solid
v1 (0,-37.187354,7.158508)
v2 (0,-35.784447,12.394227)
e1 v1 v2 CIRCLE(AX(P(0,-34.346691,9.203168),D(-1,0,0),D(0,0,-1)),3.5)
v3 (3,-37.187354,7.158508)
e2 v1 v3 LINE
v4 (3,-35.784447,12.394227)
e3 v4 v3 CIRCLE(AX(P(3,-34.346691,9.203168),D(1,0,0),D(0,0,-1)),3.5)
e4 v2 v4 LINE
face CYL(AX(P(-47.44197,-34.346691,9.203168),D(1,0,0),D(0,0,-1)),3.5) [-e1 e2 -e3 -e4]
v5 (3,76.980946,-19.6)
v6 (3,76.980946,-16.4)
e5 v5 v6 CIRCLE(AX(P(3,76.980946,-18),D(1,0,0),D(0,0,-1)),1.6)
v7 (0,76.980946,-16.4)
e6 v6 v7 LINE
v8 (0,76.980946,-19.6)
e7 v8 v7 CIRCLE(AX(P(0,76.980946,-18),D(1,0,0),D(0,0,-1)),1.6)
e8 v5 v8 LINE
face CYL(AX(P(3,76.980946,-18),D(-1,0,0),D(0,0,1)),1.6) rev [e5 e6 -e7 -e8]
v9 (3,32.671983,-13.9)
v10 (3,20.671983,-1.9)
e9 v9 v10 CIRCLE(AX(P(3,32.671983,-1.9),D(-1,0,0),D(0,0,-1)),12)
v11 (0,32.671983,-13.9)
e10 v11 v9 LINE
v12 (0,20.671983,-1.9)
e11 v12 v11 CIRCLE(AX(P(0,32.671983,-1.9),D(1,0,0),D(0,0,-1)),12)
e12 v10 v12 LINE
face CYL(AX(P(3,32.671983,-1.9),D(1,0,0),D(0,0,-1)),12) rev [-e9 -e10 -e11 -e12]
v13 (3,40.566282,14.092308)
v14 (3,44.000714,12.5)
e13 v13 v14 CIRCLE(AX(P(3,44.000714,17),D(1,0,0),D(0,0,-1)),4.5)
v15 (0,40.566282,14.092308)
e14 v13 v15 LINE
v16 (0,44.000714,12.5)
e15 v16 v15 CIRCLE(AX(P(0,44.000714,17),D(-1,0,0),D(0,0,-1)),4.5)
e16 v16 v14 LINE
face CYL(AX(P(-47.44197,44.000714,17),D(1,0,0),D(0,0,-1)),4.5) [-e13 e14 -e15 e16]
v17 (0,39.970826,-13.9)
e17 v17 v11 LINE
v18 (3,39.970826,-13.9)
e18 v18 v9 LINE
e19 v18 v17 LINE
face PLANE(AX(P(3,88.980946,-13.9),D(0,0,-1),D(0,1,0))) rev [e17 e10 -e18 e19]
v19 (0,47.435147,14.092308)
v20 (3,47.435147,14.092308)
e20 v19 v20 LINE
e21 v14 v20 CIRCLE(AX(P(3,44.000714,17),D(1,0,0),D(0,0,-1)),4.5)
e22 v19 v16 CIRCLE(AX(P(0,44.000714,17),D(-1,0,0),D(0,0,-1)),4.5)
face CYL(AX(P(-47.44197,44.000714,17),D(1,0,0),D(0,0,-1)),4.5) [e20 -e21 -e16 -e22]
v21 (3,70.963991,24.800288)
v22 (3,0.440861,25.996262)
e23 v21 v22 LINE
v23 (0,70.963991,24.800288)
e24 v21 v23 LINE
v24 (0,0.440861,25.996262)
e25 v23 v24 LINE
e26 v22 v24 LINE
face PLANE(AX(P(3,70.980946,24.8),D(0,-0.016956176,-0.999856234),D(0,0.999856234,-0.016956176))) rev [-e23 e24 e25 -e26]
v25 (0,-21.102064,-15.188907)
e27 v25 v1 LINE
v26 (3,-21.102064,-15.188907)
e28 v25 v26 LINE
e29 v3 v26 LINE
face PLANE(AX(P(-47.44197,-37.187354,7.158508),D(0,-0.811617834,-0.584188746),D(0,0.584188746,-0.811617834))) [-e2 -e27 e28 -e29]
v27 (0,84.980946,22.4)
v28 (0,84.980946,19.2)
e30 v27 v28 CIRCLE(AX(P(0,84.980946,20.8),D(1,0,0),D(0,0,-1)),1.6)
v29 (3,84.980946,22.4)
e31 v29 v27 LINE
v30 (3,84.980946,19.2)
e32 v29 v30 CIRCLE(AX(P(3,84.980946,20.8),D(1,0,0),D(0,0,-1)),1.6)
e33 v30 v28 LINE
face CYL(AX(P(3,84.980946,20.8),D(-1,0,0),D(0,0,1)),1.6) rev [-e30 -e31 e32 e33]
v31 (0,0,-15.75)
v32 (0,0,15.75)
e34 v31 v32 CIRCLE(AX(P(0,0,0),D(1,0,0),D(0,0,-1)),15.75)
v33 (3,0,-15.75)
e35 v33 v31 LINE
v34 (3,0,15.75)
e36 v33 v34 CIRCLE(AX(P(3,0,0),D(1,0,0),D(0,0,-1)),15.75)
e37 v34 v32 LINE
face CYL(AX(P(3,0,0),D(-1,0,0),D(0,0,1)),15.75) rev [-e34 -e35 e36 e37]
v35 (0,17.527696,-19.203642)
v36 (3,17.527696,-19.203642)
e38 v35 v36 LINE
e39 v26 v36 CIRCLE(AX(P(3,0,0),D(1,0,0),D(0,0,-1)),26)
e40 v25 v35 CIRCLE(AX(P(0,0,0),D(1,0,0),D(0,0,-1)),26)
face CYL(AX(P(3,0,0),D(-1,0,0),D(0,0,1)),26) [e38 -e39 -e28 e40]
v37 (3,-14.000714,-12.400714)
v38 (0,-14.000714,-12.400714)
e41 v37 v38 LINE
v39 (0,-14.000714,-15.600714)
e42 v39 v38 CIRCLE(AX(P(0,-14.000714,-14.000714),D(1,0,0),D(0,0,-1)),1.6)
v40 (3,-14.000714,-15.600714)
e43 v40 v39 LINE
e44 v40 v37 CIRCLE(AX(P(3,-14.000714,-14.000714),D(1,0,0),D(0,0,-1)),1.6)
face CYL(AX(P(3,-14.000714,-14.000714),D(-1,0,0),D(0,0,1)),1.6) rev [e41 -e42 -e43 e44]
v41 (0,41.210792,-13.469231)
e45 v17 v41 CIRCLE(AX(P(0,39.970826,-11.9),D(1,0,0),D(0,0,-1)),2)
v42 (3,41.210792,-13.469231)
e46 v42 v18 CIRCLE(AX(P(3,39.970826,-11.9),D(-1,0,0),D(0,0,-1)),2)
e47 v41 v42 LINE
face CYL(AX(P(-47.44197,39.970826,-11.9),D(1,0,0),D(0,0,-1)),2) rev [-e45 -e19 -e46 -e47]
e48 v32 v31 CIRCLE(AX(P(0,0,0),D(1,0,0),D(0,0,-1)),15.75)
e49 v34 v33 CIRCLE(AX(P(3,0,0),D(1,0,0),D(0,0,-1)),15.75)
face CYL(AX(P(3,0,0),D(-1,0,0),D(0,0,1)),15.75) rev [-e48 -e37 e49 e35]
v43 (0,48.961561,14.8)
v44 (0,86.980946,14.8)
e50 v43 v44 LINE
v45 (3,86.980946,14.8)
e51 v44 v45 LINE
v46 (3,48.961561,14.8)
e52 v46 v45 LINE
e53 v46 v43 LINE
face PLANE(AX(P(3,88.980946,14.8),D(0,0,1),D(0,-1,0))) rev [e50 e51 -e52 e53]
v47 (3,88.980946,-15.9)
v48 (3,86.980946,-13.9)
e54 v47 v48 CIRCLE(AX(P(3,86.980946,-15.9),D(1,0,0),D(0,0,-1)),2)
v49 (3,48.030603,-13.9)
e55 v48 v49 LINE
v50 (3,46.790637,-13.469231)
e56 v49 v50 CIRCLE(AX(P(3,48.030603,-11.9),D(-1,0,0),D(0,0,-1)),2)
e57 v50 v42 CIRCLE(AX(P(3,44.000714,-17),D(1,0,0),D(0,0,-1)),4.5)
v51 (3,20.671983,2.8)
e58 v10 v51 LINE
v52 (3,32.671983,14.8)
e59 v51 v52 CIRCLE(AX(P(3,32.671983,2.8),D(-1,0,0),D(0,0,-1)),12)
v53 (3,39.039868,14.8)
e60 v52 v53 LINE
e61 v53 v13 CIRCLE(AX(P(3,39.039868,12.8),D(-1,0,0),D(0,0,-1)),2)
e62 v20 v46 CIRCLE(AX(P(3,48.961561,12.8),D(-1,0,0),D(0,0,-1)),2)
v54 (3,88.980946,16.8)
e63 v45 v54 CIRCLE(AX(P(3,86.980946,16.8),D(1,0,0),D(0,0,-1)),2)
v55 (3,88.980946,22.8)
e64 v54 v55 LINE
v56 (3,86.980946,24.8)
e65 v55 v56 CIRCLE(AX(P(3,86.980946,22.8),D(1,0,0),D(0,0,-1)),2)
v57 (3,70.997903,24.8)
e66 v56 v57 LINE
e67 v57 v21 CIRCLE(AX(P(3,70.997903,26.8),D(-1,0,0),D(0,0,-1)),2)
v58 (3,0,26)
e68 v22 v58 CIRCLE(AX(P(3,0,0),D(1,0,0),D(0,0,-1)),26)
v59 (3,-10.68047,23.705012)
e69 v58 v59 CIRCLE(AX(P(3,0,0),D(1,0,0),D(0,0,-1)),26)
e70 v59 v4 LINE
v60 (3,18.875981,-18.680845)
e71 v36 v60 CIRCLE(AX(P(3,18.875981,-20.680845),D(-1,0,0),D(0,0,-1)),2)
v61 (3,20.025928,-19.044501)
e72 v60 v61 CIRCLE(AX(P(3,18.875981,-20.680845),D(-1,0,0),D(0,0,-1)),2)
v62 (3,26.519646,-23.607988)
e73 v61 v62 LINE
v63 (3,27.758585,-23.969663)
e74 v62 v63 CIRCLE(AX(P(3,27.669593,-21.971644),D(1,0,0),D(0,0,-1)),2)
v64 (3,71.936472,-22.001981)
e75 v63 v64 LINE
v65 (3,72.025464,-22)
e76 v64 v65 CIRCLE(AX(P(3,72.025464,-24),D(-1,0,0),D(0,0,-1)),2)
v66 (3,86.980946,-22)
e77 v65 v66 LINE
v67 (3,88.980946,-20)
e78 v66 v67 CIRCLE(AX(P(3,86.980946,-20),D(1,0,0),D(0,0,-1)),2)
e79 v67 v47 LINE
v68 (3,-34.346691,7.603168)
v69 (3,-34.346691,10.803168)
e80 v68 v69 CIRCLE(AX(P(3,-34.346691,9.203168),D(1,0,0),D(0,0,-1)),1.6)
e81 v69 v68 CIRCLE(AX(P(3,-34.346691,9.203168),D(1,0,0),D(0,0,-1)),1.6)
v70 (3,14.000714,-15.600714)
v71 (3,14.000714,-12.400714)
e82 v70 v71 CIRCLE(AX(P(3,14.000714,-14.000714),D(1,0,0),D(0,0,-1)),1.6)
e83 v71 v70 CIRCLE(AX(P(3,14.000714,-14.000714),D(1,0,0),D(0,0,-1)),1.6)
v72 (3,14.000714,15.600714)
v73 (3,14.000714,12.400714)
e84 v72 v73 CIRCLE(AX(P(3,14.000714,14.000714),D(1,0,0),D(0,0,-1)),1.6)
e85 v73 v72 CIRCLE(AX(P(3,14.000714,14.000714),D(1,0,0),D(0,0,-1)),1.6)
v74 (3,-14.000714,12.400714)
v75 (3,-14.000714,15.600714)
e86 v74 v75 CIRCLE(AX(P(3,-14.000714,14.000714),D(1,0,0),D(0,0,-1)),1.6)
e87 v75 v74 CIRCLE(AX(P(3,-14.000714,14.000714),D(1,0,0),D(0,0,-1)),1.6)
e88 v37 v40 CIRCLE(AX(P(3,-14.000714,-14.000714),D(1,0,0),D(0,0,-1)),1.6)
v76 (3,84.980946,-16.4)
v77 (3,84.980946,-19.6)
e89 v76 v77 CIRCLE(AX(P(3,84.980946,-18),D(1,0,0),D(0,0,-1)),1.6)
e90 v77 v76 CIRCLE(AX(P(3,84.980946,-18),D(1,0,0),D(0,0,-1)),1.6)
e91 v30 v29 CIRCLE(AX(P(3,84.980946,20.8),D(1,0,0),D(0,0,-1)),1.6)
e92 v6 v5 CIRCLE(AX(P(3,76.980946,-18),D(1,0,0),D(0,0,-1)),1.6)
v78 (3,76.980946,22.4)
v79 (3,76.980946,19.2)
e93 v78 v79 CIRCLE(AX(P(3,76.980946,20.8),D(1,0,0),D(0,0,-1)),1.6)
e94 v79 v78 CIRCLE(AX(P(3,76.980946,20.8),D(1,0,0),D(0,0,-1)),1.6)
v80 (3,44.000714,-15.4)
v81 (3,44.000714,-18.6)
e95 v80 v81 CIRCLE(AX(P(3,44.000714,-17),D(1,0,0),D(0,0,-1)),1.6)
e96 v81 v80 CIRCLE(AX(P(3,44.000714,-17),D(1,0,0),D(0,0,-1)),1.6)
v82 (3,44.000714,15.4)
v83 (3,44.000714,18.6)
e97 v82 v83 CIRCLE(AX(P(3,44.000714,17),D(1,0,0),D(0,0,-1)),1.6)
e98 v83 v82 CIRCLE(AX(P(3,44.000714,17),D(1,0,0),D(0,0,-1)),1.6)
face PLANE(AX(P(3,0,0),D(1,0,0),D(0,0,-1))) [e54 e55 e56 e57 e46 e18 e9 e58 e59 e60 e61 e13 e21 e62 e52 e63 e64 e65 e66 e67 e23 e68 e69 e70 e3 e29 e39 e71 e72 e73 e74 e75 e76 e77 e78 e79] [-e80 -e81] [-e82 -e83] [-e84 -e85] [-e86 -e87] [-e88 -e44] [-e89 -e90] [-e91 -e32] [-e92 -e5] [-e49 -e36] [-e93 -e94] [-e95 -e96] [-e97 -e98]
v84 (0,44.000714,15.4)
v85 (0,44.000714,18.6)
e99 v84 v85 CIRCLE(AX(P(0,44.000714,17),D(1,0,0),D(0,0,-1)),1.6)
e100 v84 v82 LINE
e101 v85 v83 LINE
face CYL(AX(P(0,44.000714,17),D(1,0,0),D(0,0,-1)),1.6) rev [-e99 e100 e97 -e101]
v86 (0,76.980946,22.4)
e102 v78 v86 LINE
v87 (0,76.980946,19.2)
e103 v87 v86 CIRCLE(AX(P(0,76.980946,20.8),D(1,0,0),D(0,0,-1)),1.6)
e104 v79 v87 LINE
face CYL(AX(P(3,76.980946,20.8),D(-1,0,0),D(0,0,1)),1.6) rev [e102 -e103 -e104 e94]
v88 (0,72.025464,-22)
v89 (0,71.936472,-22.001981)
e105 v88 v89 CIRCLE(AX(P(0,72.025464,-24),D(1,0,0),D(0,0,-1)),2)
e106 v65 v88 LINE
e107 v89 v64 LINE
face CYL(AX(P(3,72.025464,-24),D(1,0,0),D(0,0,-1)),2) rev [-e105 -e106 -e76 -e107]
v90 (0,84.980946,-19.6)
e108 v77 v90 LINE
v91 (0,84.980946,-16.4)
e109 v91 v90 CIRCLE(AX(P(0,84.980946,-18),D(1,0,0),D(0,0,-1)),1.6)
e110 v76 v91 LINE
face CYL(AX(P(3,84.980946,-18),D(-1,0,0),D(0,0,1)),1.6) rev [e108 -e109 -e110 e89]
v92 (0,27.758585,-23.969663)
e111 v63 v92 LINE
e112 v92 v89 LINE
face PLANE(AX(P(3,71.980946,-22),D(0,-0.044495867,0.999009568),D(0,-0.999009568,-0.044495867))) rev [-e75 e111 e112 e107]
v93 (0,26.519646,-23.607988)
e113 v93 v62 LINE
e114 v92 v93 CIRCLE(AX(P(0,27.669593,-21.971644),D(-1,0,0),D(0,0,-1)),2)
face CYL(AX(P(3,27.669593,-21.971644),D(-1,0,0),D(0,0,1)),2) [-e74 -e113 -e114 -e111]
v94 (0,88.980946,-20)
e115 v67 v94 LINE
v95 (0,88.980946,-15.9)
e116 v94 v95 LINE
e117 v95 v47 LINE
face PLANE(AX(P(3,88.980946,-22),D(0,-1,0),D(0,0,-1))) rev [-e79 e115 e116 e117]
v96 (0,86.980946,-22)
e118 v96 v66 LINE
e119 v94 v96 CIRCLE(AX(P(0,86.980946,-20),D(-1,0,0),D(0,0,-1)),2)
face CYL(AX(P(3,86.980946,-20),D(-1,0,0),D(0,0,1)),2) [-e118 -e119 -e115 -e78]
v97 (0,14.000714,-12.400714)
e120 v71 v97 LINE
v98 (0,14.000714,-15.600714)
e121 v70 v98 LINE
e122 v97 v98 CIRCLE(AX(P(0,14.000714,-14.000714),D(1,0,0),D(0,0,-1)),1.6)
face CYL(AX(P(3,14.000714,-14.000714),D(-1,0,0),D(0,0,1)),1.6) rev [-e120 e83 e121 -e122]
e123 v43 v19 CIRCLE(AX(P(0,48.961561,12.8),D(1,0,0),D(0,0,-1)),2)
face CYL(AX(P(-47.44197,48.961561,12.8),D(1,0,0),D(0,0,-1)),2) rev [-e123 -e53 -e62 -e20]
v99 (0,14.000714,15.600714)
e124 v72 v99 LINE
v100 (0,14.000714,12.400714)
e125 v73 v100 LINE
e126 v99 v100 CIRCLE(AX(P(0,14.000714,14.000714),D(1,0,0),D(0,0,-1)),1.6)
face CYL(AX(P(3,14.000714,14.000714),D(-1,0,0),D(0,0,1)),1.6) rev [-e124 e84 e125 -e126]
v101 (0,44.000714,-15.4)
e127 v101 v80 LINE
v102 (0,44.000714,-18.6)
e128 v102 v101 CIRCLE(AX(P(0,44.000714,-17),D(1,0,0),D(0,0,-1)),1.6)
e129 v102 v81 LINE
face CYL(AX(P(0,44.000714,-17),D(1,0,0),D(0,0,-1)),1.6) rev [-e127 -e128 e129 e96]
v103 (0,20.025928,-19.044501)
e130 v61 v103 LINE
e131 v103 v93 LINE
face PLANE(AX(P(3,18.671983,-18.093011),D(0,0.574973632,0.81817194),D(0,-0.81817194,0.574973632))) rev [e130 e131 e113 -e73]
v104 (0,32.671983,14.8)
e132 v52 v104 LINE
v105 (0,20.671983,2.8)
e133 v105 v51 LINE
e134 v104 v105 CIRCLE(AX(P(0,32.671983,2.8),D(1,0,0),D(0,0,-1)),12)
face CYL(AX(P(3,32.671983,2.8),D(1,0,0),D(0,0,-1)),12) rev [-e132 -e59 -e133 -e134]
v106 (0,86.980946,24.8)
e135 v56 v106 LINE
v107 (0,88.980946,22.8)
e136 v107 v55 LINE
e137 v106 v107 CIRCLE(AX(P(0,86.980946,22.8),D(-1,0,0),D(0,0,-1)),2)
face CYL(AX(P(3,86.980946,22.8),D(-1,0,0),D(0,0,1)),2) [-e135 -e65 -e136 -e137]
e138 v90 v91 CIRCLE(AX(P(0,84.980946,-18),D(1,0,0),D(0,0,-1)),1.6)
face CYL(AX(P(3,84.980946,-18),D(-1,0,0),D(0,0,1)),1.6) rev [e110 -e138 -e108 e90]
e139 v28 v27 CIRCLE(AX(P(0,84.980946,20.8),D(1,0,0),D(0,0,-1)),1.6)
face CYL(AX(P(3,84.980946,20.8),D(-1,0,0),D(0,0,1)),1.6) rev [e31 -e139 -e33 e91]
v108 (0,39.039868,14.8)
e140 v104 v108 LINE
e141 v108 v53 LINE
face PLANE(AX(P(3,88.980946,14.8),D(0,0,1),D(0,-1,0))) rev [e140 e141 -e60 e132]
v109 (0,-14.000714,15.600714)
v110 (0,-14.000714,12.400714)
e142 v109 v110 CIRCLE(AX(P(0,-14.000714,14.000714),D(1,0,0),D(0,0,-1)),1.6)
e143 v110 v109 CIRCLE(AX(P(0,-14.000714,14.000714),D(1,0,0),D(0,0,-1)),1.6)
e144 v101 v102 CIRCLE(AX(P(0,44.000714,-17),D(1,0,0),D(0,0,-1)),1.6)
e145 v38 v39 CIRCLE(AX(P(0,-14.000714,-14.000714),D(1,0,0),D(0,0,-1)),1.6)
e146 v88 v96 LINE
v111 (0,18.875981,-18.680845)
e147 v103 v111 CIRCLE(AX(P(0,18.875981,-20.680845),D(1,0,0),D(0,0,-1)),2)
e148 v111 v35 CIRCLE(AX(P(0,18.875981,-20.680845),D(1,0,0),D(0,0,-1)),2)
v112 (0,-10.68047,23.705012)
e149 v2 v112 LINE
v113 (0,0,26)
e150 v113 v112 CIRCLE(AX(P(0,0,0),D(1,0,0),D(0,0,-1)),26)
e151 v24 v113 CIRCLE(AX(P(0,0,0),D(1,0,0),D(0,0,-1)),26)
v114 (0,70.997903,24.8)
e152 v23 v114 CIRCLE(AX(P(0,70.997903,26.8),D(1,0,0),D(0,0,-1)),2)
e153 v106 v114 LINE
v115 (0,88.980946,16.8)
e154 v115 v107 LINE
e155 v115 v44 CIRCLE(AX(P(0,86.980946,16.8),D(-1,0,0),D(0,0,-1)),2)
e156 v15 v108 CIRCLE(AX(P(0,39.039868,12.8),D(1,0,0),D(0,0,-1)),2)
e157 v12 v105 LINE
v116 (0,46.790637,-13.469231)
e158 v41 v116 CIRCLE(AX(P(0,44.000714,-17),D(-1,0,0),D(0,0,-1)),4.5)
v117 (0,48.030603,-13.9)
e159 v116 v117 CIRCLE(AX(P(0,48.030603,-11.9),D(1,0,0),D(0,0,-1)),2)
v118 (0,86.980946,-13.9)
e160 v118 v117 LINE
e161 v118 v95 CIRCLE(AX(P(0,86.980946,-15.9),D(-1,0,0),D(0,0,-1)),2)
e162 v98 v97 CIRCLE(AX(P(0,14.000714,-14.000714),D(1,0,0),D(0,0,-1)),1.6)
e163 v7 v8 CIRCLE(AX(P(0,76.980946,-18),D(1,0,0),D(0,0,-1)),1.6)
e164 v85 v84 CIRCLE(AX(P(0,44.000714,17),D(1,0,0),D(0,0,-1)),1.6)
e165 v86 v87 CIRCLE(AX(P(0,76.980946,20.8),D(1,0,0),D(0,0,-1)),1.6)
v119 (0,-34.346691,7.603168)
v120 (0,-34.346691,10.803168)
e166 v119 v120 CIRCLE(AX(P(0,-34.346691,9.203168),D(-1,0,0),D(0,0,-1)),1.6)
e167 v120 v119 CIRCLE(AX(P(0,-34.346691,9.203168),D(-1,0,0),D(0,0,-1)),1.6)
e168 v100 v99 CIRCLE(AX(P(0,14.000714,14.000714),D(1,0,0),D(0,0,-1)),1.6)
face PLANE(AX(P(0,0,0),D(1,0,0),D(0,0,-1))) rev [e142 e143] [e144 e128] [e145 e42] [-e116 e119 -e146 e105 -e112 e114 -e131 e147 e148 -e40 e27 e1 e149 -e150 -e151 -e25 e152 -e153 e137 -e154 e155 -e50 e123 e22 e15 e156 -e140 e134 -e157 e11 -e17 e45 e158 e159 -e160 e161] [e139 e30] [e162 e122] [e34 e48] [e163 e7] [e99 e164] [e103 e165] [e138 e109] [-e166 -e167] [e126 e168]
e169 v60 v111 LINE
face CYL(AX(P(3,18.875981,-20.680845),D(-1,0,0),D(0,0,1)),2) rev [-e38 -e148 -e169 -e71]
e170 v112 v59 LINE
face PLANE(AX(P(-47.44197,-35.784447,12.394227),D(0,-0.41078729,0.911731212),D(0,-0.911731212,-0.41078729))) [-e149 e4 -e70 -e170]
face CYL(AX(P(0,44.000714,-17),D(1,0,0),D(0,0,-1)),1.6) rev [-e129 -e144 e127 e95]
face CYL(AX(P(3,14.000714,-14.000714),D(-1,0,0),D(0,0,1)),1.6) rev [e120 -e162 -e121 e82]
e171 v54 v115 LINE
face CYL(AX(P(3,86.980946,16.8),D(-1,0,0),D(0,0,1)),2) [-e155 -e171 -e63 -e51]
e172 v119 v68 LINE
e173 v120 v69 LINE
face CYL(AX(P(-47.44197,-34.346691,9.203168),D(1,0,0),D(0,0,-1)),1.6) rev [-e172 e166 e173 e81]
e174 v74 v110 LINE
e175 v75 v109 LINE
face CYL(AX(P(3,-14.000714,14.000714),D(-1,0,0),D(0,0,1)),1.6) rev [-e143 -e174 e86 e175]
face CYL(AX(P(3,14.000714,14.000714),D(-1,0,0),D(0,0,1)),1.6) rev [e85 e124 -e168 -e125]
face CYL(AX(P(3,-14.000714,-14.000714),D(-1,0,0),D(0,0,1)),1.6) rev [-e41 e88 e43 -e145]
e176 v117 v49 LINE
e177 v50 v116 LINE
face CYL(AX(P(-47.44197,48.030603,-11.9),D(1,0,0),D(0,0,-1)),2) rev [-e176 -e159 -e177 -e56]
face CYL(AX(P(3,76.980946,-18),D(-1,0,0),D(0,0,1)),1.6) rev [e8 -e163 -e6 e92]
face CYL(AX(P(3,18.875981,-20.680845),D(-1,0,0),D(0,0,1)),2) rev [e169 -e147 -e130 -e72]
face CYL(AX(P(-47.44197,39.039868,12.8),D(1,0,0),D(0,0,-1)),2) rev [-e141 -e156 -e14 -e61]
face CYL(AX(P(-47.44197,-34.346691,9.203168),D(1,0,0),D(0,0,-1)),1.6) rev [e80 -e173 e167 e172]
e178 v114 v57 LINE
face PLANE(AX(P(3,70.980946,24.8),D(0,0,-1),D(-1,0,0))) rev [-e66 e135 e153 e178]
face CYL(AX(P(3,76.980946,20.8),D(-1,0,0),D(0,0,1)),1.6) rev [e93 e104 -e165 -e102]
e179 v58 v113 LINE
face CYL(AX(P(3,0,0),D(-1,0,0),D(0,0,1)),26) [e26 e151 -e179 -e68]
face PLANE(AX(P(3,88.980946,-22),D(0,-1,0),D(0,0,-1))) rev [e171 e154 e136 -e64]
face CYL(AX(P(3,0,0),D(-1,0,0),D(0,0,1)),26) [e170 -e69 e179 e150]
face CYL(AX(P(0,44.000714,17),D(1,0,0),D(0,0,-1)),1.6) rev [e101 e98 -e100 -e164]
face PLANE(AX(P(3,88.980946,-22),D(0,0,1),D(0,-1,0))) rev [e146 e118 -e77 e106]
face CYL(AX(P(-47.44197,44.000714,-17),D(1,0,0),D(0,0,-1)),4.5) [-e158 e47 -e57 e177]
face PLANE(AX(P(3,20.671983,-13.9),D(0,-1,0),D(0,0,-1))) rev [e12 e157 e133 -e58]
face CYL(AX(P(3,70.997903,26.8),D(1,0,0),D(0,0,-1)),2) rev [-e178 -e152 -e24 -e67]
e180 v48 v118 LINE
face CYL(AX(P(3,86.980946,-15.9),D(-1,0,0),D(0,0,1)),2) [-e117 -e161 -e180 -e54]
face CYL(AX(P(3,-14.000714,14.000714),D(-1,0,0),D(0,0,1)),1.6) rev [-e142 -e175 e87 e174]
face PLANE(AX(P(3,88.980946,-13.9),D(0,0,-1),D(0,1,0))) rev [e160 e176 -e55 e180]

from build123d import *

# Parameters (mm, degrees)
SKETCH_1_R          = 15.75
SKETCH_1_R_2        = 1.6
EXTRUDE_1_DEPTH     = 3
SKETCH_2_W          = 28.7
SKETCH_2_H          = 68.308962896
CUT_EXTRUDE_1_DEPTH = 93.750249245
FILLET_1_R          = 12
SKETCH_4_R          = 1.6
CUT_EXTRUDE_2_DEPTH = 93.750249245
SKETCH_5_R          = 4.5
SKETCH_5_R_2        = 1.6
EXTRUDE_2_DEPTH     = 3
FILLET_2_R          = 2


with BuildPart() as part:
    # 草图1 → 凸台-拉伸1 (new body)
    with BuildSketch(Plane(origin=(0, 0, 0), x_dir=(0, 0, -1), z_dir=(1, 0, 0))):
        with BuildLine():
            Line((18.093011091, 18.671983014), (24, 27.077468597))
            Line((24, 27.077468597), (22, 71.98094591))
            Line((22, 71.98094591), (22, 88.98094591))
            Line((22, 88.98094591), (-24.8, 88.98094591))
            Line((-24.8, 88.98094591), (-24.8, 70.98094591))
            Line((-24.8, 70.98094591), (-25.996262077, 0.440860573))
            ThreePointArc((-25.996262077, 0.440860573), (9.935230264, -24.026884933), (18.093011091, 18.671983014))
        make_face()
        Circle(SKETCH_1_R, mode=Mode.SUBTRACT)
        with Locations((14.000714267, 14.000714267)):
            Circle(SKETCH_1_R_2, mode=Mode.SUBTRACT)
        with Locations((14.000714267, -14.000714267)):
            Circle(SKETCH_1_R_2, mode=Mode.SUBTRACT)
        with Locations((-14.000714267, -14.000714267)):
            Circle(SKETCH_1_R_2, mode=Mode.SUBTRACT)
        with Locations((-14.000714267, 14.000714267)):
            Circle(SKETCH_1_R_2, mode=Mode.SUBTRACT)
        with Locations((-20.8, 84.98094591)):
            Circle(SKETCH_1_R_2, mode=Mode.SUBTRACT)
        with Locations((-20.8, 76.98094591)):
            Circle(SKETCH_1_R_2, mode=Mode.SUBTRACT)
        with Locations((18, 84.98094591)):
            Circle(SKETCH_1_R_2, mode=Mode.SUBTRACT)
        with Locations((18, 76.98094591)):
            Circle(SKETCH_1_R_2, mode=Mode.SUBTRACT)
    extrude(amount=EXTRUDE_1_DEPTH)

    # 草图2 → 切除-拉伸1 (cut, through all)
    with BuildSketch(Plane.ZY):
        with Locations((0.45, 54.826464462)):
            Rectangle(SKETCH_2_W, SKETCH_2_H)
    extrude(amount=-CUT_EXTRUDE_1_DEPTH, mode=Mode.SUBTRACT)

    # 圆角1
    fillet_1_edges = [part.edges().sort_by_distance(p)[0] for p in [
        (1.5, 20.671983014, -13.9),
        (1.5, 20.671983014, 14.8),
    ]]
    fillet(fillet_1_edges, radius=FILLET_1_R)

    # 草图4 → 切除-拉伸2 (cut, through all)
    with BuildSketch(Plane(origin=(3, 0, 0), x_dir=(0, 0, -1), z_dir=(1, 0, 0))):
        with Locations((-17, 44.000714267)):
            Circle(SKETCH_4_R)
        with Locations((17, 44.000714267)):
            Circle(SKETCH_4_R)
    extrude(amount=-CUT_EXTRUDE_2_DEPTH, mode=Mode.SUBTRACT)

    # 草图5 → 凸台-拉伸2 (add)
    # profile 1 of 3: a face of its own
    with BuildSketch(Plane(origin=(3, 0, 0), x_dir=(0, 0, -1), z_dir=(1, 0, 0))):
        with Locations((-17, 44.000714267)):
            Circle(SKETCH_5_R)
        with Locations((-17, 44.000714267)):
            Circle(SKETCH_5_R_2, mode=Mode.SUBTRACT)
    # profile 2 of 3: a face of its own
    with BuildSketch(Plane(origin=(3, 0, 0), x_dir=(0, 0, -1), z_dir=(1, 0, 0))):
        with Locations((17, 44.000714267)):
            Circle(SKETCH_5_R)
        with Locations((17, 44.000714267)):
            Circle(SKETCH_5_R_2, mode=Mode.SUBTRACT)
    # profile 3 of 3: a face of its own
    with BuildSketch(Plane(origin=(3, 0, 0), x_dir=(0, 0, -1), z_dir=(1, 0, 0))):
        with BuildLine():
            Line((-12.394227472, -35.784446941), (-23.70501151, -10.680469528))
            ThreePointArc((-23.70501151, -10.680469528), (-6.729295173, -25.114071484), (15.1889074, -21.10206369))
            Line((15.1889074, -21.10206369), (-7.158507619, -37.187353847))
            ThreePointArc((-7.158507619, -37.187353847), (-10.109034889, -37.72743182), (-12.394227472, -35.784446941))
        make_face()
        with Locations((-9.203168231, -34.346691428)):
            Circle(SKETCH_5_R_2, mode=Mode.SUBTRACT)
    extrude(amount=-EXTRUDE_2_DEPTH)

    # 圆角2
    fillet_2_edges = [part.edges().sort_by_distance(p)[0] for p in [
        (1.5, 47.926271553, 14.8),
        (1.5, 40.075156982, 14.8),
        (1.5, 70.98094591, 24.8),
        (1.5, 88.98094591, 24.8),
        (1.5, 88.98094591, -22),
        (1.5, 71.98094591, -22),
        (1.5, 27.077468597, -24),
        (1.5, 40.738812981, -13.9),
        (1.5, 18.671983014, -18.093011091),
        (1.5, 47.262615554, -13.9),
        (1.5, 88.98094591, -13.9),
        (1.5, 88.98094591, 14.8),
    ]]
    fillet(fillet_2_edges, radius=FILLET_2_R)


solid = part.part
